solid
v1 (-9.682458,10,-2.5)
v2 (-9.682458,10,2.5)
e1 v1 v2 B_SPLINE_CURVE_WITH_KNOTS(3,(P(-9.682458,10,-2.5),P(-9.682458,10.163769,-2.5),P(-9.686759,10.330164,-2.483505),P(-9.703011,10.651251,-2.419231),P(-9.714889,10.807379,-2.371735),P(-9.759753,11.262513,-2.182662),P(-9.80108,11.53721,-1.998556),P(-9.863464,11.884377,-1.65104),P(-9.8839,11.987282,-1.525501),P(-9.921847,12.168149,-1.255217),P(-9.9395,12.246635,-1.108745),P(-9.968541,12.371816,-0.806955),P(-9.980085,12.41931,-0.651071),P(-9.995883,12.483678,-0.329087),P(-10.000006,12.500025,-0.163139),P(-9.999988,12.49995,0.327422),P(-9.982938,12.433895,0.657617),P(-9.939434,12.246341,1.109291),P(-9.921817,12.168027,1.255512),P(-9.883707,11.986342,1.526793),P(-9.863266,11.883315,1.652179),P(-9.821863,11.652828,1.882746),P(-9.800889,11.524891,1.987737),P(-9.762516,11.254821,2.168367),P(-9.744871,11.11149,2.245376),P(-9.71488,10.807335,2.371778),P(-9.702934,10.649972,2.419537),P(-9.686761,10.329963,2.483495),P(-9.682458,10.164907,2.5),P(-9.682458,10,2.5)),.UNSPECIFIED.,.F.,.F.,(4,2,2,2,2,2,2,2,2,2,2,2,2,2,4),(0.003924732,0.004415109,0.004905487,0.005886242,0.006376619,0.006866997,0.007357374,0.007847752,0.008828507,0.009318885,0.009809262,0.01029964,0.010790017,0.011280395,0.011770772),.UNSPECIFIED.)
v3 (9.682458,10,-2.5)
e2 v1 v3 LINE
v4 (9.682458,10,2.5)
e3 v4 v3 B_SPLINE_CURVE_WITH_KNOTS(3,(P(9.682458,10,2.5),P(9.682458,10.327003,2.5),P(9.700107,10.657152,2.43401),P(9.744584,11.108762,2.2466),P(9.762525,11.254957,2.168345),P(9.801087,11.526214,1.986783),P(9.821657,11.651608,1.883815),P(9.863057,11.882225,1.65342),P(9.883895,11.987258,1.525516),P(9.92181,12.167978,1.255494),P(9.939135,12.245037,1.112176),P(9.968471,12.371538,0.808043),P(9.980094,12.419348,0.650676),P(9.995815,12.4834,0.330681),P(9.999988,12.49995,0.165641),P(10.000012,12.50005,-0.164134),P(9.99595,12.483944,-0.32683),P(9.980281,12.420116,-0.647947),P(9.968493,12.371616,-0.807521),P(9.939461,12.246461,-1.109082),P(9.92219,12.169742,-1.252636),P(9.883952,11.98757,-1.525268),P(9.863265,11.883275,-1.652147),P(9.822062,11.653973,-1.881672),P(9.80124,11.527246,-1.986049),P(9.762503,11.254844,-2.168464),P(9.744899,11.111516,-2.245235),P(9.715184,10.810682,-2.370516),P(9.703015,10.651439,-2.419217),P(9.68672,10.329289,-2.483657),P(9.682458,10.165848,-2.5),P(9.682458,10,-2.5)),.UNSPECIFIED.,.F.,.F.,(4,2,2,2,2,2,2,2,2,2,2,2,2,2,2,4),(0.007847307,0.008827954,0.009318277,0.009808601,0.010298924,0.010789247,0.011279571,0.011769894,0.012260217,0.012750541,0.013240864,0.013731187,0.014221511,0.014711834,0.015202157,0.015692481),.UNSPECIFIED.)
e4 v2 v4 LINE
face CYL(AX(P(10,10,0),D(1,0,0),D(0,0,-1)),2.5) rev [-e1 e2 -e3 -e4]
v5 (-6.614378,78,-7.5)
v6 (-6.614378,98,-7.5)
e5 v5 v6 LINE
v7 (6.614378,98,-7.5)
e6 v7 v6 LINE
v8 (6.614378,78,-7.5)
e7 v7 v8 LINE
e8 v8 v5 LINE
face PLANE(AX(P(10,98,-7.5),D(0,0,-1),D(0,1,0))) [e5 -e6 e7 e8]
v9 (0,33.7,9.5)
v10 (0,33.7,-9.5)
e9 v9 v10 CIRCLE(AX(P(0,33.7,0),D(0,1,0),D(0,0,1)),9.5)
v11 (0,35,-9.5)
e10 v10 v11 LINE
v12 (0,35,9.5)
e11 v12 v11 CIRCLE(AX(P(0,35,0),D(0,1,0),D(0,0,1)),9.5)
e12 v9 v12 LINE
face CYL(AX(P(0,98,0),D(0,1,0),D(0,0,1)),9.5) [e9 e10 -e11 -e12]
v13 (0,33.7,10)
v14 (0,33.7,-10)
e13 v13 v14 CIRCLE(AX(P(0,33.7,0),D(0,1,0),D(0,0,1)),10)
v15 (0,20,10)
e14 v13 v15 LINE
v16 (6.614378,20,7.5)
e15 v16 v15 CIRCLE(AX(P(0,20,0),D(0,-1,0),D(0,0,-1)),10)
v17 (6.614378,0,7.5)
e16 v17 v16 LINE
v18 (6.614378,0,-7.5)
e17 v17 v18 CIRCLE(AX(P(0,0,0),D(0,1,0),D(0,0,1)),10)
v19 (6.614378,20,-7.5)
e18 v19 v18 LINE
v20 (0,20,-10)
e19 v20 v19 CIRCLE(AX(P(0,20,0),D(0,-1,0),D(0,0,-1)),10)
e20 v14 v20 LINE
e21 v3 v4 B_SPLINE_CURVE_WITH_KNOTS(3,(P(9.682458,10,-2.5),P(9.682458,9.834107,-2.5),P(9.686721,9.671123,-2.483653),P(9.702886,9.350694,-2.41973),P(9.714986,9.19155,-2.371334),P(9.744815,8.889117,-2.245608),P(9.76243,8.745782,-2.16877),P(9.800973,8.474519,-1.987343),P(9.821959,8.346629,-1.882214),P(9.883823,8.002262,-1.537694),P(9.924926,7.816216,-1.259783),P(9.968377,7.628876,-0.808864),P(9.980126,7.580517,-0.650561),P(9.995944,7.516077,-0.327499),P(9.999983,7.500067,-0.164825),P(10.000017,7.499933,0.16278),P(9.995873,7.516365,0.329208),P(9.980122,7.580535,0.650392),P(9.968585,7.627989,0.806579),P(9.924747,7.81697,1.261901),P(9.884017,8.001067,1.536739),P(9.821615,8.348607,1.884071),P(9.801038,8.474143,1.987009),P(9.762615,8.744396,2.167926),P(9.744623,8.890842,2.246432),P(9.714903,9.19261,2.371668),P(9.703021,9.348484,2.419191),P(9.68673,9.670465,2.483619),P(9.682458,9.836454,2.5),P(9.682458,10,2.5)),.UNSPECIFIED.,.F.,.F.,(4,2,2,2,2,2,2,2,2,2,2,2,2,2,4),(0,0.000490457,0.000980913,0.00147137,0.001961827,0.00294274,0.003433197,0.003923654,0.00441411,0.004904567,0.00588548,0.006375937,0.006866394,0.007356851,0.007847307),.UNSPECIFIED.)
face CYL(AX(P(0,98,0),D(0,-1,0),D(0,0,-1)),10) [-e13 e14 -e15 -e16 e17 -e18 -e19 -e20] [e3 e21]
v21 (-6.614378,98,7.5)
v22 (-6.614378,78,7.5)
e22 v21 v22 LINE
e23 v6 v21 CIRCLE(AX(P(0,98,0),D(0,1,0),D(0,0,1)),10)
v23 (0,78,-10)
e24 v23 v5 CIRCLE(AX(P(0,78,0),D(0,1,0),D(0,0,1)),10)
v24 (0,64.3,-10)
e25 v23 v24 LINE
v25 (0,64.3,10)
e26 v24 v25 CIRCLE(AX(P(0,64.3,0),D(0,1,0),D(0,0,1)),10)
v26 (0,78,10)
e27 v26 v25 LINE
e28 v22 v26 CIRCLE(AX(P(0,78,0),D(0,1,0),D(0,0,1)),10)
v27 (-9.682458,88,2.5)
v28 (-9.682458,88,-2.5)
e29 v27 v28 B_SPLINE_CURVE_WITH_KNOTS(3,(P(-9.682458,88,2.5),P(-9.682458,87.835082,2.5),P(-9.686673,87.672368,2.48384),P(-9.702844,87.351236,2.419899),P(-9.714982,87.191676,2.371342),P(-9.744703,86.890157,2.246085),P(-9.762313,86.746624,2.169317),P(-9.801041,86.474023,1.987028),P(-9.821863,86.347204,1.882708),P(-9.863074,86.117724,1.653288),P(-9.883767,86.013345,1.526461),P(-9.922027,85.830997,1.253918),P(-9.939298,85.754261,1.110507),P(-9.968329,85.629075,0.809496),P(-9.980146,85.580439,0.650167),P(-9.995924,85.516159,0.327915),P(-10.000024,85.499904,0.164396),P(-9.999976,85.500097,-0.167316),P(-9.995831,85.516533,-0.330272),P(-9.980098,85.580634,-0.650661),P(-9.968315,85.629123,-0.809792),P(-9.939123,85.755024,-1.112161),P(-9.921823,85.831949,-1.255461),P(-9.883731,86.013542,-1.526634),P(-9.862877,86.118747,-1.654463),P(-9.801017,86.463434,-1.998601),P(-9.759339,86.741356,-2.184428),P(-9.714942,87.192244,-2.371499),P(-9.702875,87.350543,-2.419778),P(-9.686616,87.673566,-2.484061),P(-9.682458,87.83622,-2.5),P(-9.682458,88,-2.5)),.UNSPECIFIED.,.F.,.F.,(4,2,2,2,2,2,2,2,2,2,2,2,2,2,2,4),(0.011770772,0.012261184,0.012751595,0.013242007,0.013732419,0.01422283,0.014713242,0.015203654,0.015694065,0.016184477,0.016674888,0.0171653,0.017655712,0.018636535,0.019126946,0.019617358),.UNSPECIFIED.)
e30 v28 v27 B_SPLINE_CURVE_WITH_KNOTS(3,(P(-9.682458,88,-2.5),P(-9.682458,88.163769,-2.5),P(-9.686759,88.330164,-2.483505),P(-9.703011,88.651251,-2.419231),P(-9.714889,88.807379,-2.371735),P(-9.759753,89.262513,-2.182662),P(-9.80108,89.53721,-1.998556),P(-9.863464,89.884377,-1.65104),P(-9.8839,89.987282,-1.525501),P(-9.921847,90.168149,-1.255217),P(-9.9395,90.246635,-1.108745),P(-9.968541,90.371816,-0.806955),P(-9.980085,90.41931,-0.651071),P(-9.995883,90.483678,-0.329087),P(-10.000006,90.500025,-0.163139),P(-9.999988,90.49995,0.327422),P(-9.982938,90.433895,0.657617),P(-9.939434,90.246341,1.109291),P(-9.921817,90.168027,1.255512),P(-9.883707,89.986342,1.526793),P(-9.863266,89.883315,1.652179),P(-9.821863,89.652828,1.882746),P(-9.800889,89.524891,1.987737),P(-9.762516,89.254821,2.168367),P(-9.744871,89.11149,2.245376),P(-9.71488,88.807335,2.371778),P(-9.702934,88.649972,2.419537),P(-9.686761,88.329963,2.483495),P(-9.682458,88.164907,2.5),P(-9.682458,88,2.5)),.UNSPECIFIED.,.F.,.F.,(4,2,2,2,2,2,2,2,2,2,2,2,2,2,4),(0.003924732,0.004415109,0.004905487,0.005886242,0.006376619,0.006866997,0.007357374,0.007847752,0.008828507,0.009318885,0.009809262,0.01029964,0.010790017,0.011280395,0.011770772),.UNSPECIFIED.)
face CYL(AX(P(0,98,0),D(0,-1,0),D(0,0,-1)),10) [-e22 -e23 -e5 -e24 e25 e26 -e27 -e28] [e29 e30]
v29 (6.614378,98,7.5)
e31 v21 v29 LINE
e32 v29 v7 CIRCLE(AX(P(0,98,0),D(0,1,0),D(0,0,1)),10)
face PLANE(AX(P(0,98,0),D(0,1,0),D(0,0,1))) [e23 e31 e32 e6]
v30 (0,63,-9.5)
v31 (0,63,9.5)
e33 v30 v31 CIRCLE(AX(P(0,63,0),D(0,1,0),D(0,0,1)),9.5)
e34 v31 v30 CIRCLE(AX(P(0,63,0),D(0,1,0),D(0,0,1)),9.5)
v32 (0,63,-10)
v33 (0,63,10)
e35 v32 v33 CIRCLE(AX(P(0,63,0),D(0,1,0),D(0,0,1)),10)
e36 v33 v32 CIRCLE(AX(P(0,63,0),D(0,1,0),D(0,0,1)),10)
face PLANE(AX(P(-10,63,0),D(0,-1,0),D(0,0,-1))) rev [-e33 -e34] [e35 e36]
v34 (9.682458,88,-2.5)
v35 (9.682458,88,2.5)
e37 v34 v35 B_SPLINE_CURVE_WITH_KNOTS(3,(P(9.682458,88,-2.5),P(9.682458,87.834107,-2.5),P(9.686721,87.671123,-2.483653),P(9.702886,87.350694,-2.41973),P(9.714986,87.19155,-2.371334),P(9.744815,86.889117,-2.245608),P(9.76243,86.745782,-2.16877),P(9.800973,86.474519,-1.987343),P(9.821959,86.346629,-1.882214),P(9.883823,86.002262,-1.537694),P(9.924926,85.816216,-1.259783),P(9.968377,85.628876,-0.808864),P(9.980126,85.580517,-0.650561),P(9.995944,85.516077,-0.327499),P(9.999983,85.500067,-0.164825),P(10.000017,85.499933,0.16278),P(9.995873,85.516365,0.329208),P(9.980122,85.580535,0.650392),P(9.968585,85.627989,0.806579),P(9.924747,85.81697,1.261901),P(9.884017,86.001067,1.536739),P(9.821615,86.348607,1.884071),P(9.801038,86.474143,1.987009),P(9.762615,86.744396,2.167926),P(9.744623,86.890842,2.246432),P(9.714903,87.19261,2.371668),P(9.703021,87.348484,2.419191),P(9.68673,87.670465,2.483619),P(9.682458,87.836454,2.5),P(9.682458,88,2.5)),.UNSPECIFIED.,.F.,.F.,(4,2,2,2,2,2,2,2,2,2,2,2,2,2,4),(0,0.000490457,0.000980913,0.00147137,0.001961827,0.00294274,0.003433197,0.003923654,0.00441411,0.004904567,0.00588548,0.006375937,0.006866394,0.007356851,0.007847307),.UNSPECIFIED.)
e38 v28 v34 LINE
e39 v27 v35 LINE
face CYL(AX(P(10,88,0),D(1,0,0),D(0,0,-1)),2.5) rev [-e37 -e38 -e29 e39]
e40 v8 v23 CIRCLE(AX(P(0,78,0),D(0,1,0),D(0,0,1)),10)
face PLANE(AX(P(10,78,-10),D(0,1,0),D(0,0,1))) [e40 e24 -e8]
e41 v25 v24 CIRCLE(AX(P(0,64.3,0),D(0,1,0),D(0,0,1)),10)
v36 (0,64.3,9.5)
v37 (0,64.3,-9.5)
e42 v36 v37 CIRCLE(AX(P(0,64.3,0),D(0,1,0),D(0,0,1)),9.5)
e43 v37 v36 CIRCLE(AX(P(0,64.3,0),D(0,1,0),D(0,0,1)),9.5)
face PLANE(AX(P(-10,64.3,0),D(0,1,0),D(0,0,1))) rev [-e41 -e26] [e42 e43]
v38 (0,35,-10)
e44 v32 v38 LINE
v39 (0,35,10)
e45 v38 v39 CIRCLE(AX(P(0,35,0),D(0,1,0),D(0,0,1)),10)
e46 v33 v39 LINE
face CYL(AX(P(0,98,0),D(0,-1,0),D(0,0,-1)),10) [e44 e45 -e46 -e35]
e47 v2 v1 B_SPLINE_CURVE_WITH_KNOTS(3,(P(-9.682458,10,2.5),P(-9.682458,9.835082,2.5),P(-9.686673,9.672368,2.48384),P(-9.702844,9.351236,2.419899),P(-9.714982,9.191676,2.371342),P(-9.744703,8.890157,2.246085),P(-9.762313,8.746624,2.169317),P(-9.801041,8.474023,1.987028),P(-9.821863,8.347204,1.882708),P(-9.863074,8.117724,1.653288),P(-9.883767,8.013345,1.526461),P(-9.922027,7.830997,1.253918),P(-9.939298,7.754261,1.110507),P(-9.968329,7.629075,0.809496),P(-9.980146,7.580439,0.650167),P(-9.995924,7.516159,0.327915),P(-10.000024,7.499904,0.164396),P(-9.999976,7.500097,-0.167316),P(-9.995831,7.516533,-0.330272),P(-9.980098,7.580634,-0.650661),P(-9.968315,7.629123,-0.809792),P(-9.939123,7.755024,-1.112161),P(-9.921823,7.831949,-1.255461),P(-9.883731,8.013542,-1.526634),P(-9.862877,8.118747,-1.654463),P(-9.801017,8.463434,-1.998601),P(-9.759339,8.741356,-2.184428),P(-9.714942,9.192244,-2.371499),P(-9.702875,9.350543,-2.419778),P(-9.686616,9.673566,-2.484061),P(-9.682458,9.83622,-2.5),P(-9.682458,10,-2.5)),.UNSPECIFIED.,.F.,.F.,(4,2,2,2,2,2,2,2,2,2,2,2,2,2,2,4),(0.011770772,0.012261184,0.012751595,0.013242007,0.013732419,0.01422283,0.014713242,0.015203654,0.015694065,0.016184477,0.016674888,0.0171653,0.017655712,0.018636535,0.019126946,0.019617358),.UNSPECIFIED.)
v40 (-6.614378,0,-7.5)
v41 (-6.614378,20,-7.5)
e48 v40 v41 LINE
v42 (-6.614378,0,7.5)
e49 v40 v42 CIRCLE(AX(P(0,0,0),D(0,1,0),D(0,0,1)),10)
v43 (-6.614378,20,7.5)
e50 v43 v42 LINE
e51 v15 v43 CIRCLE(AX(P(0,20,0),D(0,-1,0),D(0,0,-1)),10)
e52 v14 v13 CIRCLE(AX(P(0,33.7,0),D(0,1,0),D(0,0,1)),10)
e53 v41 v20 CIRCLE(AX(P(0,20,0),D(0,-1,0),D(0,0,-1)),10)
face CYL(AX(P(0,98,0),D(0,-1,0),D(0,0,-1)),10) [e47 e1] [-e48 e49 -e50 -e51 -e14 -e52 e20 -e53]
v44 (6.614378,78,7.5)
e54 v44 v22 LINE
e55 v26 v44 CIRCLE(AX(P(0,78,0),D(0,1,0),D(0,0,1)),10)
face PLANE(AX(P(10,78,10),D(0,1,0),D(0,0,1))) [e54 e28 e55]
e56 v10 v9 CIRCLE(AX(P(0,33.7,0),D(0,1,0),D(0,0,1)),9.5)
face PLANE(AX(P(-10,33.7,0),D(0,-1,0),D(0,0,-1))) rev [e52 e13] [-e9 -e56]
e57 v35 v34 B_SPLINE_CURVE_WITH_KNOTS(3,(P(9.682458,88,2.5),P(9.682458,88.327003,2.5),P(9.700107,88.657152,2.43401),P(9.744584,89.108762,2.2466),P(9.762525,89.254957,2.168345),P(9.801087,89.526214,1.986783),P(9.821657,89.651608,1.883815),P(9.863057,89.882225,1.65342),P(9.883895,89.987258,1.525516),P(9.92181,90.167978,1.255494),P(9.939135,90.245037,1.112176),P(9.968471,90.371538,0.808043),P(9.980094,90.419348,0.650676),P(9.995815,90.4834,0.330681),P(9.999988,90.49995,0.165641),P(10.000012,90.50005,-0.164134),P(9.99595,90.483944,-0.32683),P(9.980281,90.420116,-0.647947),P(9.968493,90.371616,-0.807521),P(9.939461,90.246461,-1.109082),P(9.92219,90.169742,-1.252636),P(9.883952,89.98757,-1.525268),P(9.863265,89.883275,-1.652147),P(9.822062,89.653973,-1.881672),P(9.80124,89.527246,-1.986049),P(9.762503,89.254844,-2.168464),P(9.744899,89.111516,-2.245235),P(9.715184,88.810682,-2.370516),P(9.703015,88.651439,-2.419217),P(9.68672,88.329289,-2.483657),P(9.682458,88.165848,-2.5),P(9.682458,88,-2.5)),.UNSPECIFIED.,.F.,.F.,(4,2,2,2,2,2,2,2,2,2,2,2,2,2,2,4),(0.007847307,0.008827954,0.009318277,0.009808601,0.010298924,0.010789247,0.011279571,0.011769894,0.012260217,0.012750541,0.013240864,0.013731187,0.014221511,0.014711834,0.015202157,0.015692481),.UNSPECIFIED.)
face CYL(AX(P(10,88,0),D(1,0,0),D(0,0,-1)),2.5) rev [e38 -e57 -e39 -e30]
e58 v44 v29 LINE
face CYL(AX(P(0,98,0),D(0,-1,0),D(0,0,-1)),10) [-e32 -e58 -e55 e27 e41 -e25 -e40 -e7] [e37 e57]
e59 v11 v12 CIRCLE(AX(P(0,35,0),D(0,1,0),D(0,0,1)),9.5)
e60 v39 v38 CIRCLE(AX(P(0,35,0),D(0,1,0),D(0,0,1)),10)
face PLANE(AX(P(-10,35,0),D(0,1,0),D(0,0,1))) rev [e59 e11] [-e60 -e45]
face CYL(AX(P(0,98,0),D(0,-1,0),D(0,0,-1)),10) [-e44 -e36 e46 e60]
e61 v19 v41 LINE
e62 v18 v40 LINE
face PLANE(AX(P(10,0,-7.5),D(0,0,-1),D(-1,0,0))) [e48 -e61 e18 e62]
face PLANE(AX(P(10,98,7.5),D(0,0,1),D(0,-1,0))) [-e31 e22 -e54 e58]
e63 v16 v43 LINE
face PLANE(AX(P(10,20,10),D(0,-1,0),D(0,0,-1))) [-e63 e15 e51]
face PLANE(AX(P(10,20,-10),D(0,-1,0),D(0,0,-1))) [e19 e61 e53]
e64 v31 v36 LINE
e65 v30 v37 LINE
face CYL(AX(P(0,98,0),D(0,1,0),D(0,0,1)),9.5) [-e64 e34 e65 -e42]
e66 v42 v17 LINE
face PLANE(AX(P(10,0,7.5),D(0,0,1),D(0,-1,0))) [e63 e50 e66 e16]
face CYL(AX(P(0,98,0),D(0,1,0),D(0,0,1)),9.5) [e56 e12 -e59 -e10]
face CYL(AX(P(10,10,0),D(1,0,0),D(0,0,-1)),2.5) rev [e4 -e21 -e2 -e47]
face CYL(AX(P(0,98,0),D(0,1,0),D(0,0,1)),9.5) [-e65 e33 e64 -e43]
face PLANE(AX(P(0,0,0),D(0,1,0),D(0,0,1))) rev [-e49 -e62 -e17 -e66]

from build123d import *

# Parameters (mm, degrees)
SKETCH_1_R               = 10
EXTRUDE_1_DEPTH          = 98
CUT_EXTRUDE_1_DEPTH      = 10
CUT_EXTRUDE_1_DEPTH_BACK = 10
SKETCH_2_W               = 2.5
SKETCH_2_H               = 20
HOLE_WIZARD_M6_1_D       = 5
SKETCH_5_W               = 0.5
SKETCH_5_H               = 1.3


with BuildPart() as part:
    # 草图1 → 凸台-拉伸1 (new body)
    with BuildSketch(Plane(origin=(0, 0, 0), x_dir=(1, 0, 0), z_dir=(0, 1, 0))):
        with Locations(Location((0, 0, 0), (0, 0, 270))):
            Circle(SKETCH_1_R)
    extrude(amount=EXTRUDE_1_DEPTH)

    # 草图2 → 切除-拉伸1 (cut, two sides: drawn at the far end of the back side and taken through both)
    with BuildSketch(Plane(origin=(0, 0, 0), x_dir=(0, 0, -1), z_dir=(1, 0, 0)).offset(-CUT_EXTRUDE_1_DEPTH_BACK)):
        with Locations((8.75, 88)):
            Rectangle(SKETCH_2_W, SKETCH_2_H)
        with Locations((-8.75, 88)):
            Rectangle(SKETCH_2_W, SKETCH_2_H)
        with Locations((-8.75, 10)):
            Rectangle(SKETCH_2_W, SKETCH_2_H)
        with Locations((8.75, 10)):
            Rectangle(SKETCH_2_W, SKETCH_2_H)
    extrude(amount=CUT_EXTRUDE_1_DEPTH + CUT_EXTRUDE_1_DEPTH_BACK, mode=Mode.SUBTRACT)

    # M6 螺纹孔1 (through all)
    with Locations(Plane(origin=(10, 0, 0), x_dir=(0, 0, -1), z_dir=(1, 0, 0))):
        with Locations((0, 88), (0, 10)):
            Hole(HOLE_WIZARD_M6_1_D / 2)

    # 草图5 → 切除-旋转1 (revolve, cut)
    with BuildSketch(Plane.XY, mode=Mode.PRIVATE) as cut_revolve_1_sk:
        with Locations((-9.75, 63.65)):
            Rectangle(SKETCH_5_W, SKETCH_5_H)
        with Locations((-9.75, 34.35)):
            Rectangle(SKETCH_5_W, SKETCH_5_H)
    revolve(cut_revolve_1_sk.sketch.rotate(Axis((0, 98, 0), (0, -1, 0)), 270), axis=Axis((0, 98, 0), (0, -1, 0)), mode=Mode.SUBTRACT)


solid = part.part
